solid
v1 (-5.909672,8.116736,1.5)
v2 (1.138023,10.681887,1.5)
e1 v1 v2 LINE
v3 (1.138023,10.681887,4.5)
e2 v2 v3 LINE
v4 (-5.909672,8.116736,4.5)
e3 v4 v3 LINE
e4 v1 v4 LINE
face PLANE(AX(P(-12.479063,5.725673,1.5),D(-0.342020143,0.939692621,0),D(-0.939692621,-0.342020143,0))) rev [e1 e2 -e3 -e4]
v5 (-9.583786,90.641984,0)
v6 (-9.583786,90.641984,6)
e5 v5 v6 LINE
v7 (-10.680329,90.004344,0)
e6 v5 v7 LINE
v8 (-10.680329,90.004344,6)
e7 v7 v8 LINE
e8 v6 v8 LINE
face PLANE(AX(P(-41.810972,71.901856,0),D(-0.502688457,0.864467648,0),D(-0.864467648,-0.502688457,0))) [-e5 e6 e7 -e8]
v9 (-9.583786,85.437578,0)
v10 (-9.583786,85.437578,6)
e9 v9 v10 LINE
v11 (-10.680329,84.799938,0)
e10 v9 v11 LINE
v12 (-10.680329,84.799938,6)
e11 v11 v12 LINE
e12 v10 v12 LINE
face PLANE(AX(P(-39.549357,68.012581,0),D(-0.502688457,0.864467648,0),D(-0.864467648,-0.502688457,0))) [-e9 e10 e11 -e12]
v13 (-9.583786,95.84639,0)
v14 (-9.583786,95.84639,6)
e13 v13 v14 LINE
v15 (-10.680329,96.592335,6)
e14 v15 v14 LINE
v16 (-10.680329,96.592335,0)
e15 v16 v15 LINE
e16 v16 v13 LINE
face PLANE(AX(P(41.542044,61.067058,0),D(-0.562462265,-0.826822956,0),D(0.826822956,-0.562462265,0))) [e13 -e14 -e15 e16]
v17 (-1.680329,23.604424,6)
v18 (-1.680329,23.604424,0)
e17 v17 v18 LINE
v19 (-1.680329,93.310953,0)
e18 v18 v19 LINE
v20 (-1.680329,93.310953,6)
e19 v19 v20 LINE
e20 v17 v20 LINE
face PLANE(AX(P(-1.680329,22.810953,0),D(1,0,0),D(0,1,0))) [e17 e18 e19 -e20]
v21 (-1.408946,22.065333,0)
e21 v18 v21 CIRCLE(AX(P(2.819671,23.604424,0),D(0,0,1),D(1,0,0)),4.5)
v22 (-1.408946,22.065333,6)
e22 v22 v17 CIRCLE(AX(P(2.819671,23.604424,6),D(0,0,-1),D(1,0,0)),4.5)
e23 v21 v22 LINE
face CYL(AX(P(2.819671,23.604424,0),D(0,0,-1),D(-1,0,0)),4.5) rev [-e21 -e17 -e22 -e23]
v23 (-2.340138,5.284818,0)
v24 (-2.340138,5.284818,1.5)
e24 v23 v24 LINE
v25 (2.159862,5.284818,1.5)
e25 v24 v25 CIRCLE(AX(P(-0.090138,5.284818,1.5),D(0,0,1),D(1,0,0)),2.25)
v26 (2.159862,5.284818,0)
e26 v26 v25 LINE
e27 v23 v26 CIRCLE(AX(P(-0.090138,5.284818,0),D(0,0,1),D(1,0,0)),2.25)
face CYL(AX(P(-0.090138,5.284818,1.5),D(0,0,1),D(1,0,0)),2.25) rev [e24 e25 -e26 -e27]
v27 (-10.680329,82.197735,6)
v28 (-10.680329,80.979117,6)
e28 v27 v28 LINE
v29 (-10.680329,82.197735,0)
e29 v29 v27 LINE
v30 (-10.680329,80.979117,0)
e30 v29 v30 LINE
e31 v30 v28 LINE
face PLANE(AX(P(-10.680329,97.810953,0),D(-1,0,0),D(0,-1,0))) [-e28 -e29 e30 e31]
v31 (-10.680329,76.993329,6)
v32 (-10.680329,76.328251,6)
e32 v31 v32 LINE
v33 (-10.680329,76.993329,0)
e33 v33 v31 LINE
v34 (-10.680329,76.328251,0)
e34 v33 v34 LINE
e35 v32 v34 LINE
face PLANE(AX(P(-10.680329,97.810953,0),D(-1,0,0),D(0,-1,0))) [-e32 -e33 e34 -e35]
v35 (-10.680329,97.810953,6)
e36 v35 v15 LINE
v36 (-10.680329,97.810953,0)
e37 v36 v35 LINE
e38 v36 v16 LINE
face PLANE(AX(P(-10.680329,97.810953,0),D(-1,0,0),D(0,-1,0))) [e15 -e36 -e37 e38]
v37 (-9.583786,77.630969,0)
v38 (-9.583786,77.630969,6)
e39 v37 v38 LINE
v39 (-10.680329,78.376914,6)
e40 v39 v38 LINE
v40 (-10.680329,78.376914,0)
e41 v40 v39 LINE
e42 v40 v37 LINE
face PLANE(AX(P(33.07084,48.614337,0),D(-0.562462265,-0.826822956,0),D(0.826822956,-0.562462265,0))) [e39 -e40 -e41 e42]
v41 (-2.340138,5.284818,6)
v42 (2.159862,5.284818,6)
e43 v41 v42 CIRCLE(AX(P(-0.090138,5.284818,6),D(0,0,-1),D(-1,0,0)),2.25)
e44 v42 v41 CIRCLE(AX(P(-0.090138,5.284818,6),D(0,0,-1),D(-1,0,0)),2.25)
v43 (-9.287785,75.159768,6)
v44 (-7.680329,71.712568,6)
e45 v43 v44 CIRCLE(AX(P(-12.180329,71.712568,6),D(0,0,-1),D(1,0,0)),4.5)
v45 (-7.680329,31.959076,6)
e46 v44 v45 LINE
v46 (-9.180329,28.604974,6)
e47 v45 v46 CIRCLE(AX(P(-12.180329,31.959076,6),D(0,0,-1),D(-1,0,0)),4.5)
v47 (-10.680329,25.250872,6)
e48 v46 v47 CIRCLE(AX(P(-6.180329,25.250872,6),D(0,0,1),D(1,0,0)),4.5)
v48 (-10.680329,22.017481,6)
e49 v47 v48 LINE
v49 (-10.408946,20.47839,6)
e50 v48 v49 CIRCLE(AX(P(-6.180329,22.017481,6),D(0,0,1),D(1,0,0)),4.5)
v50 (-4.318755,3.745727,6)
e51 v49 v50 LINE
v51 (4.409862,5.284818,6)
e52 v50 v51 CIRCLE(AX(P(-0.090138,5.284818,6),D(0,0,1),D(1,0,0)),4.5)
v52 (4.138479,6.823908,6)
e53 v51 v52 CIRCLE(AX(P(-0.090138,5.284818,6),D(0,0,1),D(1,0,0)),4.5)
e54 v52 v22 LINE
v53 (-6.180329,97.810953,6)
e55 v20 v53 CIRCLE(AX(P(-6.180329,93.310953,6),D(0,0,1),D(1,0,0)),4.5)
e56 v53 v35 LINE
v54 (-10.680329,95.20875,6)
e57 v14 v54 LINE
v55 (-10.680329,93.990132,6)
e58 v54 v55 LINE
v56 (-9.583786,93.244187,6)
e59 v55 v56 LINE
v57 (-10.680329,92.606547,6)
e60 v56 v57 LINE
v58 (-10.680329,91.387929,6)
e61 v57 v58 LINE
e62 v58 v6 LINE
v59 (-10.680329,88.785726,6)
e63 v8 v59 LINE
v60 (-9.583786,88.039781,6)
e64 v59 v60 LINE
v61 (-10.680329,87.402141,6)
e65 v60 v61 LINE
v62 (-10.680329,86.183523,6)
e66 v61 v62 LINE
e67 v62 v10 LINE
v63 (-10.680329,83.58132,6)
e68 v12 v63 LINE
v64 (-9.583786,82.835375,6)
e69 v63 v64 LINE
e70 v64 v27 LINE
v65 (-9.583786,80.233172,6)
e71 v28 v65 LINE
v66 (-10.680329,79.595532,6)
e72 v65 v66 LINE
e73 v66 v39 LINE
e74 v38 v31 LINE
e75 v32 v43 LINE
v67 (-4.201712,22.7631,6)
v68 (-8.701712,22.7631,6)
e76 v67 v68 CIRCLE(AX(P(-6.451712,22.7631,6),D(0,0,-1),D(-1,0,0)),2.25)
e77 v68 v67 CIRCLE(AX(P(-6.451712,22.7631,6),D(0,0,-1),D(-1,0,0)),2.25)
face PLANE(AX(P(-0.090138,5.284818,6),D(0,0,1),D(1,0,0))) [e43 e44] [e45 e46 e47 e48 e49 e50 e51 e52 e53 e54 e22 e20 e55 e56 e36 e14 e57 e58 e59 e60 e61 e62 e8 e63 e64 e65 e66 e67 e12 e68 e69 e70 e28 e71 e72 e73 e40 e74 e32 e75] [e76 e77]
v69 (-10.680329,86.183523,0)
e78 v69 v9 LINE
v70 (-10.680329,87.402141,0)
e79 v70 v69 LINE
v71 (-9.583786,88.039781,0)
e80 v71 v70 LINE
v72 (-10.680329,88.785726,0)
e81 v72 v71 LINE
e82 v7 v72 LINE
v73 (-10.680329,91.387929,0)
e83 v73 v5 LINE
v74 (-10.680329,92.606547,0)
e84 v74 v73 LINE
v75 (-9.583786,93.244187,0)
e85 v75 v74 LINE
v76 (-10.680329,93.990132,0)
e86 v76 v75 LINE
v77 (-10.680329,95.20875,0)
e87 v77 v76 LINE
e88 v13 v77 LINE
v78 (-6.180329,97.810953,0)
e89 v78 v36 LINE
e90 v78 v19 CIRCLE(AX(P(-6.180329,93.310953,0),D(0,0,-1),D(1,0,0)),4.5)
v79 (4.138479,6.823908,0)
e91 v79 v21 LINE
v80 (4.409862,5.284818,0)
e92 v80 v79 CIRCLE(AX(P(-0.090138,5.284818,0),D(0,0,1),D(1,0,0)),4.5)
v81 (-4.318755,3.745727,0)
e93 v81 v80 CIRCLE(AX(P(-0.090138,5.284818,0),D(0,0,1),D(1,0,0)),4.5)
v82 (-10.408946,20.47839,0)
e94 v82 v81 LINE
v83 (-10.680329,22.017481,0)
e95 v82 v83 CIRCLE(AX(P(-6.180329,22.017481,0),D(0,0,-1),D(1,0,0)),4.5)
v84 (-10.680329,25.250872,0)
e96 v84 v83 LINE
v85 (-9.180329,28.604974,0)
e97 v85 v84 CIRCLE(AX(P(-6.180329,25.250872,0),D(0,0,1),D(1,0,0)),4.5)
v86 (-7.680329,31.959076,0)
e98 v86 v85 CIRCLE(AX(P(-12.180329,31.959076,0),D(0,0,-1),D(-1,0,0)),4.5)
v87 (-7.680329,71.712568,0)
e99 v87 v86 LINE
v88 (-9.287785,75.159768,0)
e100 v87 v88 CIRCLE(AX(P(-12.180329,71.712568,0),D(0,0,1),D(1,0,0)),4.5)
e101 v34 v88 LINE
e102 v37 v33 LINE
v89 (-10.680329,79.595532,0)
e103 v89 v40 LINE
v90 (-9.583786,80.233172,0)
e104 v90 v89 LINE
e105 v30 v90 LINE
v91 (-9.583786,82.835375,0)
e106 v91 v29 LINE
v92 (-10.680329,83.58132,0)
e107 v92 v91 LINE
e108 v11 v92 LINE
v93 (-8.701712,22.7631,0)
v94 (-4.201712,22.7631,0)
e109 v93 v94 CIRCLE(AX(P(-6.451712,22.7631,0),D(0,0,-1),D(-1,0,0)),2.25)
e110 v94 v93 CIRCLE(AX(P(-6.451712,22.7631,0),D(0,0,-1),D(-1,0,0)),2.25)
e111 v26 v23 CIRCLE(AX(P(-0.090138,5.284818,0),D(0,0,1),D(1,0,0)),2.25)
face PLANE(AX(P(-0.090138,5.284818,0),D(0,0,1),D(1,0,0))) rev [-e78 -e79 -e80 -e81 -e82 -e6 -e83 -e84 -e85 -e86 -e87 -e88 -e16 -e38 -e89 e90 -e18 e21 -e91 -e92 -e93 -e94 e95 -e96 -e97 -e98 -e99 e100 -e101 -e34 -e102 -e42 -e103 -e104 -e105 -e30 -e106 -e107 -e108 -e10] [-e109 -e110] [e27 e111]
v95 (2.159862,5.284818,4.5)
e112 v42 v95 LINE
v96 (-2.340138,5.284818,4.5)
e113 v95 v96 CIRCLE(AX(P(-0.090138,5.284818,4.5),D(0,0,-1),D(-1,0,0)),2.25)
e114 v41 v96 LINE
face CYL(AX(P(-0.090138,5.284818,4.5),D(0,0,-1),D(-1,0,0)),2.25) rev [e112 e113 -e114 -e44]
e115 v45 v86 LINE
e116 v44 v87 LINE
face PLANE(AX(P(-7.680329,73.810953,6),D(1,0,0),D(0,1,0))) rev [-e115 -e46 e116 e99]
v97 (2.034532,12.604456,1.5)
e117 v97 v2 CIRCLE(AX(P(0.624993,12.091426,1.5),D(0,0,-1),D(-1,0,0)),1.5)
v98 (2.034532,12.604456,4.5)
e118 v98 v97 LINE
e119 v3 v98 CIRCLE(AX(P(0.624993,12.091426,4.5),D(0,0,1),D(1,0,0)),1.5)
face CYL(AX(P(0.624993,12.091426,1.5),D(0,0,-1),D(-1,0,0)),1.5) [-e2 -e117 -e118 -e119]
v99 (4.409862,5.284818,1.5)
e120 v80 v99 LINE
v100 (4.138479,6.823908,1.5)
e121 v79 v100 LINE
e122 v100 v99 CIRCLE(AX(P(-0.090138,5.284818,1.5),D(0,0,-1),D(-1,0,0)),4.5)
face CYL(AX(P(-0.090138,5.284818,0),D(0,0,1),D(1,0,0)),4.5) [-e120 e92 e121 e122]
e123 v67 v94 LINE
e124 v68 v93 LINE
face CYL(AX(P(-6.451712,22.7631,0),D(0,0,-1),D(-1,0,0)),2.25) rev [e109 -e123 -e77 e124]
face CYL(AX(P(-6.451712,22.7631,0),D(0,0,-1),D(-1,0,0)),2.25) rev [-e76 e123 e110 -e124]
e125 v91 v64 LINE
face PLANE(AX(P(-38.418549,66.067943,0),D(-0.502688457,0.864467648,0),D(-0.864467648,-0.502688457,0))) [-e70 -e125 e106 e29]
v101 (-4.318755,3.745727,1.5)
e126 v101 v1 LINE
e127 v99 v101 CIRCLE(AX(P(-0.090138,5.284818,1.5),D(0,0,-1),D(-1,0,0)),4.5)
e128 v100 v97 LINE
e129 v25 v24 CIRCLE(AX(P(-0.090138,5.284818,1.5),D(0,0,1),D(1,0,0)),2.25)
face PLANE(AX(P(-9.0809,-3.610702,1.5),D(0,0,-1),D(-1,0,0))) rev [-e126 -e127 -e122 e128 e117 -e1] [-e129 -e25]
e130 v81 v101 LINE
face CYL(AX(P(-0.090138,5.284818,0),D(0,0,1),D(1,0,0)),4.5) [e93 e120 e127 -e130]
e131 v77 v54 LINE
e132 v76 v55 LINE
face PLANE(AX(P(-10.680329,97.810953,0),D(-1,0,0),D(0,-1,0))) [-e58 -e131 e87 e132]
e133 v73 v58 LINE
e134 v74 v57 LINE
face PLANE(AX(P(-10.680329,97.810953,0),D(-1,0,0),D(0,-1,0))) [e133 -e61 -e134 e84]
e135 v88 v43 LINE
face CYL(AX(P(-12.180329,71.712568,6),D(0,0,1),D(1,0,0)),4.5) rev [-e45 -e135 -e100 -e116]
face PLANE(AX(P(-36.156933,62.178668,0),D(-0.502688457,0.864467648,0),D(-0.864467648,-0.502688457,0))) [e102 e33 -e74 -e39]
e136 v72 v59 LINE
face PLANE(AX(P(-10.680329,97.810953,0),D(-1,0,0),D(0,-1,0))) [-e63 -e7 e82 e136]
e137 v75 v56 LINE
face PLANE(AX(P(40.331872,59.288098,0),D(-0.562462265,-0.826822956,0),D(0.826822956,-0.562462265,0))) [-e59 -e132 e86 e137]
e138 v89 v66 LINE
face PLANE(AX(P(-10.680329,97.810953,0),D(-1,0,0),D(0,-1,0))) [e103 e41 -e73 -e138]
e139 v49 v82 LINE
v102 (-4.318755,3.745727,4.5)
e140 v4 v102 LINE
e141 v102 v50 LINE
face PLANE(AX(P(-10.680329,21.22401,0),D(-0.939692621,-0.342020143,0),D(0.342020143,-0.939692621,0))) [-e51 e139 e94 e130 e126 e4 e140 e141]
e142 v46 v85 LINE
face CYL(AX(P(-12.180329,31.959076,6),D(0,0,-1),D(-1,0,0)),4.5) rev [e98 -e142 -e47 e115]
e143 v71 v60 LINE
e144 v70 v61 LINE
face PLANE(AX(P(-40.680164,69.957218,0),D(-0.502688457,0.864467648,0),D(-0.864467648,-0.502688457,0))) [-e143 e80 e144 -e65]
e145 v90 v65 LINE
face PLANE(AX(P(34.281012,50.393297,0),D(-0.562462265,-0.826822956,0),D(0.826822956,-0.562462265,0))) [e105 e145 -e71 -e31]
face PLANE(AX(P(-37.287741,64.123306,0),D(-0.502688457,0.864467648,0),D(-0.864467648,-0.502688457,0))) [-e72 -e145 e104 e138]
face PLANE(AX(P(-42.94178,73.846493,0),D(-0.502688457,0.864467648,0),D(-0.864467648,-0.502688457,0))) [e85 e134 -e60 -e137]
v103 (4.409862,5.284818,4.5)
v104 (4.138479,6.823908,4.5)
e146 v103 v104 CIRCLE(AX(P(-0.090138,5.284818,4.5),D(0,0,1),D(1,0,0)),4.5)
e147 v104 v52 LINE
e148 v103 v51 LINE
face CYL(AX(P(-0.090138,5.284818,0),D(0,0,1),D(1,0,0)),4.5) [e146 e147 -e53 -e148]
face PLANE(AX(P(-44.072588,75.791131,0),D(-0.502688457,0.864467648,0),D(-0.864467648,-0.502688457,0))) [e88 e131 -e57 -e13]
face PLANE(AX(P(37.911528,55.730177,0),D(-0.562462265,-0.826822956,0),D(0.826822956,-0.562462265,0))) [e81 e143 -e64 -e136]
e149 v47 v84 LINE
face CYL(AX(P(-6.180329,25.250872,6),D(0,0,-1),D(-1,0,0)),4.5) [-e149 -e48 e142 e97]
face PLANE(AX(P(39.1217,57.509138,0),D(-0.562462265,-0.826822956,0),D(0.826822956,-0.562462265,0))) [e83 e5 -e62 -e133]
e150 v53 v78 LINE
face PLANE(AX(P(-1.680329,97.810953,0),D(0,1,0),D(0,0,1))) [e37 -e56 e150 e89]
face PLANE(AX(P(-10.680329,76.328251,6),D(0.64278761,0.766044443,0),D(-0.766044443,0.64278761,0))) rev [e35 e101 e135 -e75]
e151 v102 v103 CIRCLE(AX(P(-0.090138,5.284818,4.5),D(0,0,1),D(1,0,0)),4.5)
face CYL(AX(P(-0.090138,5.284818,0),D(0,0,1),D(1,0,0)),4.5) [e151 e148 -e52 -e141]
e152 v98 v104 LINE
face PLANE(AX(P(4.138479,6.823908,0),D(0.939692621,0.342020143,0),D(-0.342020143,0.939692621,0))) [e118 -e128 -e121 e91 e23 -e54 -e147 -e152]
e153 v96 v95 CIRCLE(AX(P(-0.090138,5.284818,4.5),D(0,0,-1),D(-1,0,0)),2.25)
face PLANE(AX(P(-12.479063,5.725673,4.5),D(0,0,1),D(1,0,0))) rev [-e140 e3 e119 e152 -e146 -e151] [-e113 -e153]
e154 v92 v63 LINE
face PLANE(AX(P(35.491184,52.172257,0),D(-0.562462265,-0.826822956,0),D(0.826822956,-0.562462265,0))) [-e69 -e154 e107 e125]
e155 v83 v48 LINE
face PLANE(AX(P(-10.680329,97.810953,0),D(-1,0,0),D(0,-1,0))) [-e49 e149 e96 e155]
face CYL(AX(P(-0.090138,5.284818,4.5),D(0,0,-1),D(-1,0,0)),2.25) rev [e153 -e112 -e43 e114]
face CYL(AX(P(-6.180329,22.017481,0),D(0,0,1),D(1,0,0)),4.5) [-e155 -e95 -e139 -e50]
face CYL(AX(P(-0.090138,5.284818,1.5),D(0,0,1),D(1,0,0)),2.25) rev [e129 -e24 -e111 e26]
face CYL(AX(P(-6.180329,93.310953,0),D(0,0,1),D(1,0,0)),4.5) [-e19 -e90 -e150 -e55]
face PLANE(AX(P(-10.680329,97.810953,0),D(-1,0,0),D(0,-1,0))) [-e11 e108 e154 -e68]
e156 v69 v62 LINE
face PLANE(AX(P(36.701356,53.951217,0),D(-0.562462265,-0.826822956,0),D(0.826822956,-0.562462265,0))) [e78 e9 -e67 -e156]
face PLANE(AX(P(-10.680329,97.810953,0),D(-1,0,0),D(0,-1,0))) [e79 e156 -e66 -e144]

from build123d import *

# Parameters (mm, degrees)
BOSS_EXTRUDE1_DEPTH            = 20
CUT_EXTRUDE1_REACH             = 326.283
SKETCH2_W                      = 10
SKETCH2_H                      = 33.118542384
CUT_EXTRUDE2_DEPTH             = 329.583692554
F_15_0_15_DIAMETER_HOLE1_D     = 15
F_15_0_15_DIAMETER_HOLE1_DEPTH = 5
F_15_0_15_DIAMETER_HOLE2_D     = 15
F_15_0_15_DIAMETER_HOLE3_D     = 15
FILLET1_R                      = 5
FILLET2_R                      = 15
CUT_EXTRUDE3_DEPTH             = 20
SCALE1_SCALE                   = 0.3


with BuildPart() as part:
    # Sketch1 → Boss-Extrude1 (new body)
    with BuildSketch(Plane.XY.offset(20)):
        with BuildLine():
            Line((-35.601097413, 326.0365085), (-35.601097413, 70.746699079))
            Line((-35.601097413, 70.746699079), (-14.395848526, 12.48575659))
            ThreePointArc((-14.395848526, 12.48575659), (4.829842935, 3.520669429), (13.794930097, 22.74636089))
            Line((13.794930097, 22.74636089), (-5.601097413, 76.0365085))
            Line((-5.601097413, 76.0365085), (-5.601097413, 326.0365085))
            Line((-5.601097413, 326.0365085), (-35.601097413, 326.0365085))
        make_face()
    extrude(amount=-BOSS_EXTRUDE1_DEPTH)

    # Sketch2 → Cut-Extrude1 (cut, up to next)
    with BuildSketch(Plane(origin=(19.491769294, 7.094423836, 0), x_dir=(0, 0, -1), z_dir=(0.9396926207859105, 0.3420201433256631, 0)), mode=Mode.PRIVATE) as cut_extrude1_sk1:
        with Locations((-10, 15.602274889)):
            Rectangle(SKETCH2_W, SKETCH2_H)
    cut_extrude1_tool1 = extrude(cut_extrude1_sk1.sketch, amount=-CUT_EXTRUDE1_REACH, mode=Mode.PRIVATE) & part.part
    add(cut_extrude1_tool1.solids().sort_by_distance((14.155477, 21.755766, 10))[0], mode=Mode.SUBTRACT)

    # Sketch3 → Cut-Extrude2 (cut, through all)
    with BuildSketch(Plane(origin=(0, 0, 0), x_dir=(-1, 0, 0), z_dir=(0, 0, -1))):
        with BuildLine():
            Line((35.601097413, 84.169572779), (35.601097413, 254.427504812))
            Line((35.601097413, 254.427504812), (25.601097413, 246.0365085))
            Line((25.601097413, 246.0365085), (25.601097413, 106.530252554))
            ThreePointArc((25.601097413, 106.530252554), (26.908033475, 100.406528198), (30.601097413, 95.349912667))
            ThreePointArc((30.601097413, 95.349912667), (34.29416135, 90.293297136), (35.601097413, 84.169572779))
        make_face()
    extrude(amount=-CUT_EXTRUDE2_DEPTH, mode=Mode.SUBTRACT)

    # Ø15.0 (15) Diameter Hole1
    with Locations(Plane.XY.offset(5)):
        with Locations((-0.300459215, 17.61605874)):
            Hole(F_15_0_15_DIAMETER_HOLE1_D / 2, depth=F_15_0_15_DIAMETER_HOLE1_DEPTH)

    # Ø15.0 (15) Diameter Hole2 (through all)
    with Locations(Plane(origin=(0, 0, 0), x_dir=(-1, 0, 0), z_dir=(0, 0, -1))):
        with Locations((21.505708101, 75.877001229)):
            Hole(F_15_0_15_DIAMETER_HOLE2_D / 2)

    # Ø15.0 (15) Diameter Hole3 (through all)
    with Locations(Plane(origin=(0, 0, 15), x_dir=(-1, 0, 0), z_dir=(0, 0, -1))):
        with Locations((0.300459215, 17.61605874)):
            Hole(F_15_0_15_DIAMETER_HOLE3_D / 2)

    # Fillet1
    fillet1_edges = [part.edges().sort_by_distance(p)[0] for p in [
        (8.491872693, 37.316391362, 10),
    ]]
    fillet(fillet1_edges, radius=FILLET1_R)

    # Fillet2
    fillet2_edges = [part.edges().sort_by_distance(p)[0] for p in [
        (-5.601097413, 326.0365085, 10),
        (-5.601097413, 76.0365085, 10),
        (-35.601097413, 70.746699079, 10),
        (-25.601097413, 246.0365085, 10),
    ]]
    fillet(fillet2_edges, radius=FILLET2_R)

    # Sketch10 → Cut-Extrude3 (cut)
    with BuildSketch(Plane.XY.offset(20)):
        Polygon((-35.601097413, 317.362498495), (-35.601097413, 321.974448946), (-35.601097413, 326.0365085), (-41.358567597, 326.0365085), (-41.358567597, 256.644428456), (-35.601097413, 256.644428456), (-35.601097413, 261.256378908), (-35.601097413, 265.318438462), (-35.601097413, 269.930388913), (-35.601097413, 273.992448467), (-35.601097413, 278.604398919), (-35.601097413, 282.666458473), (-35.601097413, 287.278408924), (-35.601097413, 291.340468478), (-35.601097413, 295.95241893), (-35.601097413, 300.014478484), (-35.601097413, 304.626428935), (-35.601097413, 308.688488489), (-35.601097413, 313.300438941), align=None)
        Polygon((-31.945953564, 310.813956834), (-35.601097413, 313.300438941), (-35.601097413, 308.688488489), align=None)
        Polygon((-31.945953564, 319.487966839), (-35.601097413, 321.974448946), (-35.601097413, 317.362498495), align=None)
        Polygon((-31.945953564, 302.139946828), (-35.601097413, 304.626428935), (-35.601097413, 300.014478484), align=None)
        Polygon((-31.945953564, 293.465936823), (-35.601097413, 295.95241893), (-35.601097413, 291.340468478), align=None)
        Polygon((-31.945953564, 284.791926817), (-35.601097413, 287.278408924), (-35.601097413, 282.666458473), align=None)
        Polygon((-35.601097413, 278.604398919), (-35.601097413, 273.992448467), (-31.945953564, 276.117916812), align=None)
        Polygon((-35.601097413, 269.930388913), (-35.601097413, 265.318438462), (-31.945953564, 267.443906806), align=None)
        Polygon((-35.601097413, 261.256378908), (-35.601097413, 256.644428456), (-31.945953564, 258.769896801), align=None)
    extrude(amount=-CUT_EXTRUDE3_DEPTH, mode=Mode.SUBTRACT)


with BuildPart() as part_1:
    # Scale1: scaled about (0, 0, 0)
    add(part.part.scale(SCALE1_SCALE))


solid = part_1.part
